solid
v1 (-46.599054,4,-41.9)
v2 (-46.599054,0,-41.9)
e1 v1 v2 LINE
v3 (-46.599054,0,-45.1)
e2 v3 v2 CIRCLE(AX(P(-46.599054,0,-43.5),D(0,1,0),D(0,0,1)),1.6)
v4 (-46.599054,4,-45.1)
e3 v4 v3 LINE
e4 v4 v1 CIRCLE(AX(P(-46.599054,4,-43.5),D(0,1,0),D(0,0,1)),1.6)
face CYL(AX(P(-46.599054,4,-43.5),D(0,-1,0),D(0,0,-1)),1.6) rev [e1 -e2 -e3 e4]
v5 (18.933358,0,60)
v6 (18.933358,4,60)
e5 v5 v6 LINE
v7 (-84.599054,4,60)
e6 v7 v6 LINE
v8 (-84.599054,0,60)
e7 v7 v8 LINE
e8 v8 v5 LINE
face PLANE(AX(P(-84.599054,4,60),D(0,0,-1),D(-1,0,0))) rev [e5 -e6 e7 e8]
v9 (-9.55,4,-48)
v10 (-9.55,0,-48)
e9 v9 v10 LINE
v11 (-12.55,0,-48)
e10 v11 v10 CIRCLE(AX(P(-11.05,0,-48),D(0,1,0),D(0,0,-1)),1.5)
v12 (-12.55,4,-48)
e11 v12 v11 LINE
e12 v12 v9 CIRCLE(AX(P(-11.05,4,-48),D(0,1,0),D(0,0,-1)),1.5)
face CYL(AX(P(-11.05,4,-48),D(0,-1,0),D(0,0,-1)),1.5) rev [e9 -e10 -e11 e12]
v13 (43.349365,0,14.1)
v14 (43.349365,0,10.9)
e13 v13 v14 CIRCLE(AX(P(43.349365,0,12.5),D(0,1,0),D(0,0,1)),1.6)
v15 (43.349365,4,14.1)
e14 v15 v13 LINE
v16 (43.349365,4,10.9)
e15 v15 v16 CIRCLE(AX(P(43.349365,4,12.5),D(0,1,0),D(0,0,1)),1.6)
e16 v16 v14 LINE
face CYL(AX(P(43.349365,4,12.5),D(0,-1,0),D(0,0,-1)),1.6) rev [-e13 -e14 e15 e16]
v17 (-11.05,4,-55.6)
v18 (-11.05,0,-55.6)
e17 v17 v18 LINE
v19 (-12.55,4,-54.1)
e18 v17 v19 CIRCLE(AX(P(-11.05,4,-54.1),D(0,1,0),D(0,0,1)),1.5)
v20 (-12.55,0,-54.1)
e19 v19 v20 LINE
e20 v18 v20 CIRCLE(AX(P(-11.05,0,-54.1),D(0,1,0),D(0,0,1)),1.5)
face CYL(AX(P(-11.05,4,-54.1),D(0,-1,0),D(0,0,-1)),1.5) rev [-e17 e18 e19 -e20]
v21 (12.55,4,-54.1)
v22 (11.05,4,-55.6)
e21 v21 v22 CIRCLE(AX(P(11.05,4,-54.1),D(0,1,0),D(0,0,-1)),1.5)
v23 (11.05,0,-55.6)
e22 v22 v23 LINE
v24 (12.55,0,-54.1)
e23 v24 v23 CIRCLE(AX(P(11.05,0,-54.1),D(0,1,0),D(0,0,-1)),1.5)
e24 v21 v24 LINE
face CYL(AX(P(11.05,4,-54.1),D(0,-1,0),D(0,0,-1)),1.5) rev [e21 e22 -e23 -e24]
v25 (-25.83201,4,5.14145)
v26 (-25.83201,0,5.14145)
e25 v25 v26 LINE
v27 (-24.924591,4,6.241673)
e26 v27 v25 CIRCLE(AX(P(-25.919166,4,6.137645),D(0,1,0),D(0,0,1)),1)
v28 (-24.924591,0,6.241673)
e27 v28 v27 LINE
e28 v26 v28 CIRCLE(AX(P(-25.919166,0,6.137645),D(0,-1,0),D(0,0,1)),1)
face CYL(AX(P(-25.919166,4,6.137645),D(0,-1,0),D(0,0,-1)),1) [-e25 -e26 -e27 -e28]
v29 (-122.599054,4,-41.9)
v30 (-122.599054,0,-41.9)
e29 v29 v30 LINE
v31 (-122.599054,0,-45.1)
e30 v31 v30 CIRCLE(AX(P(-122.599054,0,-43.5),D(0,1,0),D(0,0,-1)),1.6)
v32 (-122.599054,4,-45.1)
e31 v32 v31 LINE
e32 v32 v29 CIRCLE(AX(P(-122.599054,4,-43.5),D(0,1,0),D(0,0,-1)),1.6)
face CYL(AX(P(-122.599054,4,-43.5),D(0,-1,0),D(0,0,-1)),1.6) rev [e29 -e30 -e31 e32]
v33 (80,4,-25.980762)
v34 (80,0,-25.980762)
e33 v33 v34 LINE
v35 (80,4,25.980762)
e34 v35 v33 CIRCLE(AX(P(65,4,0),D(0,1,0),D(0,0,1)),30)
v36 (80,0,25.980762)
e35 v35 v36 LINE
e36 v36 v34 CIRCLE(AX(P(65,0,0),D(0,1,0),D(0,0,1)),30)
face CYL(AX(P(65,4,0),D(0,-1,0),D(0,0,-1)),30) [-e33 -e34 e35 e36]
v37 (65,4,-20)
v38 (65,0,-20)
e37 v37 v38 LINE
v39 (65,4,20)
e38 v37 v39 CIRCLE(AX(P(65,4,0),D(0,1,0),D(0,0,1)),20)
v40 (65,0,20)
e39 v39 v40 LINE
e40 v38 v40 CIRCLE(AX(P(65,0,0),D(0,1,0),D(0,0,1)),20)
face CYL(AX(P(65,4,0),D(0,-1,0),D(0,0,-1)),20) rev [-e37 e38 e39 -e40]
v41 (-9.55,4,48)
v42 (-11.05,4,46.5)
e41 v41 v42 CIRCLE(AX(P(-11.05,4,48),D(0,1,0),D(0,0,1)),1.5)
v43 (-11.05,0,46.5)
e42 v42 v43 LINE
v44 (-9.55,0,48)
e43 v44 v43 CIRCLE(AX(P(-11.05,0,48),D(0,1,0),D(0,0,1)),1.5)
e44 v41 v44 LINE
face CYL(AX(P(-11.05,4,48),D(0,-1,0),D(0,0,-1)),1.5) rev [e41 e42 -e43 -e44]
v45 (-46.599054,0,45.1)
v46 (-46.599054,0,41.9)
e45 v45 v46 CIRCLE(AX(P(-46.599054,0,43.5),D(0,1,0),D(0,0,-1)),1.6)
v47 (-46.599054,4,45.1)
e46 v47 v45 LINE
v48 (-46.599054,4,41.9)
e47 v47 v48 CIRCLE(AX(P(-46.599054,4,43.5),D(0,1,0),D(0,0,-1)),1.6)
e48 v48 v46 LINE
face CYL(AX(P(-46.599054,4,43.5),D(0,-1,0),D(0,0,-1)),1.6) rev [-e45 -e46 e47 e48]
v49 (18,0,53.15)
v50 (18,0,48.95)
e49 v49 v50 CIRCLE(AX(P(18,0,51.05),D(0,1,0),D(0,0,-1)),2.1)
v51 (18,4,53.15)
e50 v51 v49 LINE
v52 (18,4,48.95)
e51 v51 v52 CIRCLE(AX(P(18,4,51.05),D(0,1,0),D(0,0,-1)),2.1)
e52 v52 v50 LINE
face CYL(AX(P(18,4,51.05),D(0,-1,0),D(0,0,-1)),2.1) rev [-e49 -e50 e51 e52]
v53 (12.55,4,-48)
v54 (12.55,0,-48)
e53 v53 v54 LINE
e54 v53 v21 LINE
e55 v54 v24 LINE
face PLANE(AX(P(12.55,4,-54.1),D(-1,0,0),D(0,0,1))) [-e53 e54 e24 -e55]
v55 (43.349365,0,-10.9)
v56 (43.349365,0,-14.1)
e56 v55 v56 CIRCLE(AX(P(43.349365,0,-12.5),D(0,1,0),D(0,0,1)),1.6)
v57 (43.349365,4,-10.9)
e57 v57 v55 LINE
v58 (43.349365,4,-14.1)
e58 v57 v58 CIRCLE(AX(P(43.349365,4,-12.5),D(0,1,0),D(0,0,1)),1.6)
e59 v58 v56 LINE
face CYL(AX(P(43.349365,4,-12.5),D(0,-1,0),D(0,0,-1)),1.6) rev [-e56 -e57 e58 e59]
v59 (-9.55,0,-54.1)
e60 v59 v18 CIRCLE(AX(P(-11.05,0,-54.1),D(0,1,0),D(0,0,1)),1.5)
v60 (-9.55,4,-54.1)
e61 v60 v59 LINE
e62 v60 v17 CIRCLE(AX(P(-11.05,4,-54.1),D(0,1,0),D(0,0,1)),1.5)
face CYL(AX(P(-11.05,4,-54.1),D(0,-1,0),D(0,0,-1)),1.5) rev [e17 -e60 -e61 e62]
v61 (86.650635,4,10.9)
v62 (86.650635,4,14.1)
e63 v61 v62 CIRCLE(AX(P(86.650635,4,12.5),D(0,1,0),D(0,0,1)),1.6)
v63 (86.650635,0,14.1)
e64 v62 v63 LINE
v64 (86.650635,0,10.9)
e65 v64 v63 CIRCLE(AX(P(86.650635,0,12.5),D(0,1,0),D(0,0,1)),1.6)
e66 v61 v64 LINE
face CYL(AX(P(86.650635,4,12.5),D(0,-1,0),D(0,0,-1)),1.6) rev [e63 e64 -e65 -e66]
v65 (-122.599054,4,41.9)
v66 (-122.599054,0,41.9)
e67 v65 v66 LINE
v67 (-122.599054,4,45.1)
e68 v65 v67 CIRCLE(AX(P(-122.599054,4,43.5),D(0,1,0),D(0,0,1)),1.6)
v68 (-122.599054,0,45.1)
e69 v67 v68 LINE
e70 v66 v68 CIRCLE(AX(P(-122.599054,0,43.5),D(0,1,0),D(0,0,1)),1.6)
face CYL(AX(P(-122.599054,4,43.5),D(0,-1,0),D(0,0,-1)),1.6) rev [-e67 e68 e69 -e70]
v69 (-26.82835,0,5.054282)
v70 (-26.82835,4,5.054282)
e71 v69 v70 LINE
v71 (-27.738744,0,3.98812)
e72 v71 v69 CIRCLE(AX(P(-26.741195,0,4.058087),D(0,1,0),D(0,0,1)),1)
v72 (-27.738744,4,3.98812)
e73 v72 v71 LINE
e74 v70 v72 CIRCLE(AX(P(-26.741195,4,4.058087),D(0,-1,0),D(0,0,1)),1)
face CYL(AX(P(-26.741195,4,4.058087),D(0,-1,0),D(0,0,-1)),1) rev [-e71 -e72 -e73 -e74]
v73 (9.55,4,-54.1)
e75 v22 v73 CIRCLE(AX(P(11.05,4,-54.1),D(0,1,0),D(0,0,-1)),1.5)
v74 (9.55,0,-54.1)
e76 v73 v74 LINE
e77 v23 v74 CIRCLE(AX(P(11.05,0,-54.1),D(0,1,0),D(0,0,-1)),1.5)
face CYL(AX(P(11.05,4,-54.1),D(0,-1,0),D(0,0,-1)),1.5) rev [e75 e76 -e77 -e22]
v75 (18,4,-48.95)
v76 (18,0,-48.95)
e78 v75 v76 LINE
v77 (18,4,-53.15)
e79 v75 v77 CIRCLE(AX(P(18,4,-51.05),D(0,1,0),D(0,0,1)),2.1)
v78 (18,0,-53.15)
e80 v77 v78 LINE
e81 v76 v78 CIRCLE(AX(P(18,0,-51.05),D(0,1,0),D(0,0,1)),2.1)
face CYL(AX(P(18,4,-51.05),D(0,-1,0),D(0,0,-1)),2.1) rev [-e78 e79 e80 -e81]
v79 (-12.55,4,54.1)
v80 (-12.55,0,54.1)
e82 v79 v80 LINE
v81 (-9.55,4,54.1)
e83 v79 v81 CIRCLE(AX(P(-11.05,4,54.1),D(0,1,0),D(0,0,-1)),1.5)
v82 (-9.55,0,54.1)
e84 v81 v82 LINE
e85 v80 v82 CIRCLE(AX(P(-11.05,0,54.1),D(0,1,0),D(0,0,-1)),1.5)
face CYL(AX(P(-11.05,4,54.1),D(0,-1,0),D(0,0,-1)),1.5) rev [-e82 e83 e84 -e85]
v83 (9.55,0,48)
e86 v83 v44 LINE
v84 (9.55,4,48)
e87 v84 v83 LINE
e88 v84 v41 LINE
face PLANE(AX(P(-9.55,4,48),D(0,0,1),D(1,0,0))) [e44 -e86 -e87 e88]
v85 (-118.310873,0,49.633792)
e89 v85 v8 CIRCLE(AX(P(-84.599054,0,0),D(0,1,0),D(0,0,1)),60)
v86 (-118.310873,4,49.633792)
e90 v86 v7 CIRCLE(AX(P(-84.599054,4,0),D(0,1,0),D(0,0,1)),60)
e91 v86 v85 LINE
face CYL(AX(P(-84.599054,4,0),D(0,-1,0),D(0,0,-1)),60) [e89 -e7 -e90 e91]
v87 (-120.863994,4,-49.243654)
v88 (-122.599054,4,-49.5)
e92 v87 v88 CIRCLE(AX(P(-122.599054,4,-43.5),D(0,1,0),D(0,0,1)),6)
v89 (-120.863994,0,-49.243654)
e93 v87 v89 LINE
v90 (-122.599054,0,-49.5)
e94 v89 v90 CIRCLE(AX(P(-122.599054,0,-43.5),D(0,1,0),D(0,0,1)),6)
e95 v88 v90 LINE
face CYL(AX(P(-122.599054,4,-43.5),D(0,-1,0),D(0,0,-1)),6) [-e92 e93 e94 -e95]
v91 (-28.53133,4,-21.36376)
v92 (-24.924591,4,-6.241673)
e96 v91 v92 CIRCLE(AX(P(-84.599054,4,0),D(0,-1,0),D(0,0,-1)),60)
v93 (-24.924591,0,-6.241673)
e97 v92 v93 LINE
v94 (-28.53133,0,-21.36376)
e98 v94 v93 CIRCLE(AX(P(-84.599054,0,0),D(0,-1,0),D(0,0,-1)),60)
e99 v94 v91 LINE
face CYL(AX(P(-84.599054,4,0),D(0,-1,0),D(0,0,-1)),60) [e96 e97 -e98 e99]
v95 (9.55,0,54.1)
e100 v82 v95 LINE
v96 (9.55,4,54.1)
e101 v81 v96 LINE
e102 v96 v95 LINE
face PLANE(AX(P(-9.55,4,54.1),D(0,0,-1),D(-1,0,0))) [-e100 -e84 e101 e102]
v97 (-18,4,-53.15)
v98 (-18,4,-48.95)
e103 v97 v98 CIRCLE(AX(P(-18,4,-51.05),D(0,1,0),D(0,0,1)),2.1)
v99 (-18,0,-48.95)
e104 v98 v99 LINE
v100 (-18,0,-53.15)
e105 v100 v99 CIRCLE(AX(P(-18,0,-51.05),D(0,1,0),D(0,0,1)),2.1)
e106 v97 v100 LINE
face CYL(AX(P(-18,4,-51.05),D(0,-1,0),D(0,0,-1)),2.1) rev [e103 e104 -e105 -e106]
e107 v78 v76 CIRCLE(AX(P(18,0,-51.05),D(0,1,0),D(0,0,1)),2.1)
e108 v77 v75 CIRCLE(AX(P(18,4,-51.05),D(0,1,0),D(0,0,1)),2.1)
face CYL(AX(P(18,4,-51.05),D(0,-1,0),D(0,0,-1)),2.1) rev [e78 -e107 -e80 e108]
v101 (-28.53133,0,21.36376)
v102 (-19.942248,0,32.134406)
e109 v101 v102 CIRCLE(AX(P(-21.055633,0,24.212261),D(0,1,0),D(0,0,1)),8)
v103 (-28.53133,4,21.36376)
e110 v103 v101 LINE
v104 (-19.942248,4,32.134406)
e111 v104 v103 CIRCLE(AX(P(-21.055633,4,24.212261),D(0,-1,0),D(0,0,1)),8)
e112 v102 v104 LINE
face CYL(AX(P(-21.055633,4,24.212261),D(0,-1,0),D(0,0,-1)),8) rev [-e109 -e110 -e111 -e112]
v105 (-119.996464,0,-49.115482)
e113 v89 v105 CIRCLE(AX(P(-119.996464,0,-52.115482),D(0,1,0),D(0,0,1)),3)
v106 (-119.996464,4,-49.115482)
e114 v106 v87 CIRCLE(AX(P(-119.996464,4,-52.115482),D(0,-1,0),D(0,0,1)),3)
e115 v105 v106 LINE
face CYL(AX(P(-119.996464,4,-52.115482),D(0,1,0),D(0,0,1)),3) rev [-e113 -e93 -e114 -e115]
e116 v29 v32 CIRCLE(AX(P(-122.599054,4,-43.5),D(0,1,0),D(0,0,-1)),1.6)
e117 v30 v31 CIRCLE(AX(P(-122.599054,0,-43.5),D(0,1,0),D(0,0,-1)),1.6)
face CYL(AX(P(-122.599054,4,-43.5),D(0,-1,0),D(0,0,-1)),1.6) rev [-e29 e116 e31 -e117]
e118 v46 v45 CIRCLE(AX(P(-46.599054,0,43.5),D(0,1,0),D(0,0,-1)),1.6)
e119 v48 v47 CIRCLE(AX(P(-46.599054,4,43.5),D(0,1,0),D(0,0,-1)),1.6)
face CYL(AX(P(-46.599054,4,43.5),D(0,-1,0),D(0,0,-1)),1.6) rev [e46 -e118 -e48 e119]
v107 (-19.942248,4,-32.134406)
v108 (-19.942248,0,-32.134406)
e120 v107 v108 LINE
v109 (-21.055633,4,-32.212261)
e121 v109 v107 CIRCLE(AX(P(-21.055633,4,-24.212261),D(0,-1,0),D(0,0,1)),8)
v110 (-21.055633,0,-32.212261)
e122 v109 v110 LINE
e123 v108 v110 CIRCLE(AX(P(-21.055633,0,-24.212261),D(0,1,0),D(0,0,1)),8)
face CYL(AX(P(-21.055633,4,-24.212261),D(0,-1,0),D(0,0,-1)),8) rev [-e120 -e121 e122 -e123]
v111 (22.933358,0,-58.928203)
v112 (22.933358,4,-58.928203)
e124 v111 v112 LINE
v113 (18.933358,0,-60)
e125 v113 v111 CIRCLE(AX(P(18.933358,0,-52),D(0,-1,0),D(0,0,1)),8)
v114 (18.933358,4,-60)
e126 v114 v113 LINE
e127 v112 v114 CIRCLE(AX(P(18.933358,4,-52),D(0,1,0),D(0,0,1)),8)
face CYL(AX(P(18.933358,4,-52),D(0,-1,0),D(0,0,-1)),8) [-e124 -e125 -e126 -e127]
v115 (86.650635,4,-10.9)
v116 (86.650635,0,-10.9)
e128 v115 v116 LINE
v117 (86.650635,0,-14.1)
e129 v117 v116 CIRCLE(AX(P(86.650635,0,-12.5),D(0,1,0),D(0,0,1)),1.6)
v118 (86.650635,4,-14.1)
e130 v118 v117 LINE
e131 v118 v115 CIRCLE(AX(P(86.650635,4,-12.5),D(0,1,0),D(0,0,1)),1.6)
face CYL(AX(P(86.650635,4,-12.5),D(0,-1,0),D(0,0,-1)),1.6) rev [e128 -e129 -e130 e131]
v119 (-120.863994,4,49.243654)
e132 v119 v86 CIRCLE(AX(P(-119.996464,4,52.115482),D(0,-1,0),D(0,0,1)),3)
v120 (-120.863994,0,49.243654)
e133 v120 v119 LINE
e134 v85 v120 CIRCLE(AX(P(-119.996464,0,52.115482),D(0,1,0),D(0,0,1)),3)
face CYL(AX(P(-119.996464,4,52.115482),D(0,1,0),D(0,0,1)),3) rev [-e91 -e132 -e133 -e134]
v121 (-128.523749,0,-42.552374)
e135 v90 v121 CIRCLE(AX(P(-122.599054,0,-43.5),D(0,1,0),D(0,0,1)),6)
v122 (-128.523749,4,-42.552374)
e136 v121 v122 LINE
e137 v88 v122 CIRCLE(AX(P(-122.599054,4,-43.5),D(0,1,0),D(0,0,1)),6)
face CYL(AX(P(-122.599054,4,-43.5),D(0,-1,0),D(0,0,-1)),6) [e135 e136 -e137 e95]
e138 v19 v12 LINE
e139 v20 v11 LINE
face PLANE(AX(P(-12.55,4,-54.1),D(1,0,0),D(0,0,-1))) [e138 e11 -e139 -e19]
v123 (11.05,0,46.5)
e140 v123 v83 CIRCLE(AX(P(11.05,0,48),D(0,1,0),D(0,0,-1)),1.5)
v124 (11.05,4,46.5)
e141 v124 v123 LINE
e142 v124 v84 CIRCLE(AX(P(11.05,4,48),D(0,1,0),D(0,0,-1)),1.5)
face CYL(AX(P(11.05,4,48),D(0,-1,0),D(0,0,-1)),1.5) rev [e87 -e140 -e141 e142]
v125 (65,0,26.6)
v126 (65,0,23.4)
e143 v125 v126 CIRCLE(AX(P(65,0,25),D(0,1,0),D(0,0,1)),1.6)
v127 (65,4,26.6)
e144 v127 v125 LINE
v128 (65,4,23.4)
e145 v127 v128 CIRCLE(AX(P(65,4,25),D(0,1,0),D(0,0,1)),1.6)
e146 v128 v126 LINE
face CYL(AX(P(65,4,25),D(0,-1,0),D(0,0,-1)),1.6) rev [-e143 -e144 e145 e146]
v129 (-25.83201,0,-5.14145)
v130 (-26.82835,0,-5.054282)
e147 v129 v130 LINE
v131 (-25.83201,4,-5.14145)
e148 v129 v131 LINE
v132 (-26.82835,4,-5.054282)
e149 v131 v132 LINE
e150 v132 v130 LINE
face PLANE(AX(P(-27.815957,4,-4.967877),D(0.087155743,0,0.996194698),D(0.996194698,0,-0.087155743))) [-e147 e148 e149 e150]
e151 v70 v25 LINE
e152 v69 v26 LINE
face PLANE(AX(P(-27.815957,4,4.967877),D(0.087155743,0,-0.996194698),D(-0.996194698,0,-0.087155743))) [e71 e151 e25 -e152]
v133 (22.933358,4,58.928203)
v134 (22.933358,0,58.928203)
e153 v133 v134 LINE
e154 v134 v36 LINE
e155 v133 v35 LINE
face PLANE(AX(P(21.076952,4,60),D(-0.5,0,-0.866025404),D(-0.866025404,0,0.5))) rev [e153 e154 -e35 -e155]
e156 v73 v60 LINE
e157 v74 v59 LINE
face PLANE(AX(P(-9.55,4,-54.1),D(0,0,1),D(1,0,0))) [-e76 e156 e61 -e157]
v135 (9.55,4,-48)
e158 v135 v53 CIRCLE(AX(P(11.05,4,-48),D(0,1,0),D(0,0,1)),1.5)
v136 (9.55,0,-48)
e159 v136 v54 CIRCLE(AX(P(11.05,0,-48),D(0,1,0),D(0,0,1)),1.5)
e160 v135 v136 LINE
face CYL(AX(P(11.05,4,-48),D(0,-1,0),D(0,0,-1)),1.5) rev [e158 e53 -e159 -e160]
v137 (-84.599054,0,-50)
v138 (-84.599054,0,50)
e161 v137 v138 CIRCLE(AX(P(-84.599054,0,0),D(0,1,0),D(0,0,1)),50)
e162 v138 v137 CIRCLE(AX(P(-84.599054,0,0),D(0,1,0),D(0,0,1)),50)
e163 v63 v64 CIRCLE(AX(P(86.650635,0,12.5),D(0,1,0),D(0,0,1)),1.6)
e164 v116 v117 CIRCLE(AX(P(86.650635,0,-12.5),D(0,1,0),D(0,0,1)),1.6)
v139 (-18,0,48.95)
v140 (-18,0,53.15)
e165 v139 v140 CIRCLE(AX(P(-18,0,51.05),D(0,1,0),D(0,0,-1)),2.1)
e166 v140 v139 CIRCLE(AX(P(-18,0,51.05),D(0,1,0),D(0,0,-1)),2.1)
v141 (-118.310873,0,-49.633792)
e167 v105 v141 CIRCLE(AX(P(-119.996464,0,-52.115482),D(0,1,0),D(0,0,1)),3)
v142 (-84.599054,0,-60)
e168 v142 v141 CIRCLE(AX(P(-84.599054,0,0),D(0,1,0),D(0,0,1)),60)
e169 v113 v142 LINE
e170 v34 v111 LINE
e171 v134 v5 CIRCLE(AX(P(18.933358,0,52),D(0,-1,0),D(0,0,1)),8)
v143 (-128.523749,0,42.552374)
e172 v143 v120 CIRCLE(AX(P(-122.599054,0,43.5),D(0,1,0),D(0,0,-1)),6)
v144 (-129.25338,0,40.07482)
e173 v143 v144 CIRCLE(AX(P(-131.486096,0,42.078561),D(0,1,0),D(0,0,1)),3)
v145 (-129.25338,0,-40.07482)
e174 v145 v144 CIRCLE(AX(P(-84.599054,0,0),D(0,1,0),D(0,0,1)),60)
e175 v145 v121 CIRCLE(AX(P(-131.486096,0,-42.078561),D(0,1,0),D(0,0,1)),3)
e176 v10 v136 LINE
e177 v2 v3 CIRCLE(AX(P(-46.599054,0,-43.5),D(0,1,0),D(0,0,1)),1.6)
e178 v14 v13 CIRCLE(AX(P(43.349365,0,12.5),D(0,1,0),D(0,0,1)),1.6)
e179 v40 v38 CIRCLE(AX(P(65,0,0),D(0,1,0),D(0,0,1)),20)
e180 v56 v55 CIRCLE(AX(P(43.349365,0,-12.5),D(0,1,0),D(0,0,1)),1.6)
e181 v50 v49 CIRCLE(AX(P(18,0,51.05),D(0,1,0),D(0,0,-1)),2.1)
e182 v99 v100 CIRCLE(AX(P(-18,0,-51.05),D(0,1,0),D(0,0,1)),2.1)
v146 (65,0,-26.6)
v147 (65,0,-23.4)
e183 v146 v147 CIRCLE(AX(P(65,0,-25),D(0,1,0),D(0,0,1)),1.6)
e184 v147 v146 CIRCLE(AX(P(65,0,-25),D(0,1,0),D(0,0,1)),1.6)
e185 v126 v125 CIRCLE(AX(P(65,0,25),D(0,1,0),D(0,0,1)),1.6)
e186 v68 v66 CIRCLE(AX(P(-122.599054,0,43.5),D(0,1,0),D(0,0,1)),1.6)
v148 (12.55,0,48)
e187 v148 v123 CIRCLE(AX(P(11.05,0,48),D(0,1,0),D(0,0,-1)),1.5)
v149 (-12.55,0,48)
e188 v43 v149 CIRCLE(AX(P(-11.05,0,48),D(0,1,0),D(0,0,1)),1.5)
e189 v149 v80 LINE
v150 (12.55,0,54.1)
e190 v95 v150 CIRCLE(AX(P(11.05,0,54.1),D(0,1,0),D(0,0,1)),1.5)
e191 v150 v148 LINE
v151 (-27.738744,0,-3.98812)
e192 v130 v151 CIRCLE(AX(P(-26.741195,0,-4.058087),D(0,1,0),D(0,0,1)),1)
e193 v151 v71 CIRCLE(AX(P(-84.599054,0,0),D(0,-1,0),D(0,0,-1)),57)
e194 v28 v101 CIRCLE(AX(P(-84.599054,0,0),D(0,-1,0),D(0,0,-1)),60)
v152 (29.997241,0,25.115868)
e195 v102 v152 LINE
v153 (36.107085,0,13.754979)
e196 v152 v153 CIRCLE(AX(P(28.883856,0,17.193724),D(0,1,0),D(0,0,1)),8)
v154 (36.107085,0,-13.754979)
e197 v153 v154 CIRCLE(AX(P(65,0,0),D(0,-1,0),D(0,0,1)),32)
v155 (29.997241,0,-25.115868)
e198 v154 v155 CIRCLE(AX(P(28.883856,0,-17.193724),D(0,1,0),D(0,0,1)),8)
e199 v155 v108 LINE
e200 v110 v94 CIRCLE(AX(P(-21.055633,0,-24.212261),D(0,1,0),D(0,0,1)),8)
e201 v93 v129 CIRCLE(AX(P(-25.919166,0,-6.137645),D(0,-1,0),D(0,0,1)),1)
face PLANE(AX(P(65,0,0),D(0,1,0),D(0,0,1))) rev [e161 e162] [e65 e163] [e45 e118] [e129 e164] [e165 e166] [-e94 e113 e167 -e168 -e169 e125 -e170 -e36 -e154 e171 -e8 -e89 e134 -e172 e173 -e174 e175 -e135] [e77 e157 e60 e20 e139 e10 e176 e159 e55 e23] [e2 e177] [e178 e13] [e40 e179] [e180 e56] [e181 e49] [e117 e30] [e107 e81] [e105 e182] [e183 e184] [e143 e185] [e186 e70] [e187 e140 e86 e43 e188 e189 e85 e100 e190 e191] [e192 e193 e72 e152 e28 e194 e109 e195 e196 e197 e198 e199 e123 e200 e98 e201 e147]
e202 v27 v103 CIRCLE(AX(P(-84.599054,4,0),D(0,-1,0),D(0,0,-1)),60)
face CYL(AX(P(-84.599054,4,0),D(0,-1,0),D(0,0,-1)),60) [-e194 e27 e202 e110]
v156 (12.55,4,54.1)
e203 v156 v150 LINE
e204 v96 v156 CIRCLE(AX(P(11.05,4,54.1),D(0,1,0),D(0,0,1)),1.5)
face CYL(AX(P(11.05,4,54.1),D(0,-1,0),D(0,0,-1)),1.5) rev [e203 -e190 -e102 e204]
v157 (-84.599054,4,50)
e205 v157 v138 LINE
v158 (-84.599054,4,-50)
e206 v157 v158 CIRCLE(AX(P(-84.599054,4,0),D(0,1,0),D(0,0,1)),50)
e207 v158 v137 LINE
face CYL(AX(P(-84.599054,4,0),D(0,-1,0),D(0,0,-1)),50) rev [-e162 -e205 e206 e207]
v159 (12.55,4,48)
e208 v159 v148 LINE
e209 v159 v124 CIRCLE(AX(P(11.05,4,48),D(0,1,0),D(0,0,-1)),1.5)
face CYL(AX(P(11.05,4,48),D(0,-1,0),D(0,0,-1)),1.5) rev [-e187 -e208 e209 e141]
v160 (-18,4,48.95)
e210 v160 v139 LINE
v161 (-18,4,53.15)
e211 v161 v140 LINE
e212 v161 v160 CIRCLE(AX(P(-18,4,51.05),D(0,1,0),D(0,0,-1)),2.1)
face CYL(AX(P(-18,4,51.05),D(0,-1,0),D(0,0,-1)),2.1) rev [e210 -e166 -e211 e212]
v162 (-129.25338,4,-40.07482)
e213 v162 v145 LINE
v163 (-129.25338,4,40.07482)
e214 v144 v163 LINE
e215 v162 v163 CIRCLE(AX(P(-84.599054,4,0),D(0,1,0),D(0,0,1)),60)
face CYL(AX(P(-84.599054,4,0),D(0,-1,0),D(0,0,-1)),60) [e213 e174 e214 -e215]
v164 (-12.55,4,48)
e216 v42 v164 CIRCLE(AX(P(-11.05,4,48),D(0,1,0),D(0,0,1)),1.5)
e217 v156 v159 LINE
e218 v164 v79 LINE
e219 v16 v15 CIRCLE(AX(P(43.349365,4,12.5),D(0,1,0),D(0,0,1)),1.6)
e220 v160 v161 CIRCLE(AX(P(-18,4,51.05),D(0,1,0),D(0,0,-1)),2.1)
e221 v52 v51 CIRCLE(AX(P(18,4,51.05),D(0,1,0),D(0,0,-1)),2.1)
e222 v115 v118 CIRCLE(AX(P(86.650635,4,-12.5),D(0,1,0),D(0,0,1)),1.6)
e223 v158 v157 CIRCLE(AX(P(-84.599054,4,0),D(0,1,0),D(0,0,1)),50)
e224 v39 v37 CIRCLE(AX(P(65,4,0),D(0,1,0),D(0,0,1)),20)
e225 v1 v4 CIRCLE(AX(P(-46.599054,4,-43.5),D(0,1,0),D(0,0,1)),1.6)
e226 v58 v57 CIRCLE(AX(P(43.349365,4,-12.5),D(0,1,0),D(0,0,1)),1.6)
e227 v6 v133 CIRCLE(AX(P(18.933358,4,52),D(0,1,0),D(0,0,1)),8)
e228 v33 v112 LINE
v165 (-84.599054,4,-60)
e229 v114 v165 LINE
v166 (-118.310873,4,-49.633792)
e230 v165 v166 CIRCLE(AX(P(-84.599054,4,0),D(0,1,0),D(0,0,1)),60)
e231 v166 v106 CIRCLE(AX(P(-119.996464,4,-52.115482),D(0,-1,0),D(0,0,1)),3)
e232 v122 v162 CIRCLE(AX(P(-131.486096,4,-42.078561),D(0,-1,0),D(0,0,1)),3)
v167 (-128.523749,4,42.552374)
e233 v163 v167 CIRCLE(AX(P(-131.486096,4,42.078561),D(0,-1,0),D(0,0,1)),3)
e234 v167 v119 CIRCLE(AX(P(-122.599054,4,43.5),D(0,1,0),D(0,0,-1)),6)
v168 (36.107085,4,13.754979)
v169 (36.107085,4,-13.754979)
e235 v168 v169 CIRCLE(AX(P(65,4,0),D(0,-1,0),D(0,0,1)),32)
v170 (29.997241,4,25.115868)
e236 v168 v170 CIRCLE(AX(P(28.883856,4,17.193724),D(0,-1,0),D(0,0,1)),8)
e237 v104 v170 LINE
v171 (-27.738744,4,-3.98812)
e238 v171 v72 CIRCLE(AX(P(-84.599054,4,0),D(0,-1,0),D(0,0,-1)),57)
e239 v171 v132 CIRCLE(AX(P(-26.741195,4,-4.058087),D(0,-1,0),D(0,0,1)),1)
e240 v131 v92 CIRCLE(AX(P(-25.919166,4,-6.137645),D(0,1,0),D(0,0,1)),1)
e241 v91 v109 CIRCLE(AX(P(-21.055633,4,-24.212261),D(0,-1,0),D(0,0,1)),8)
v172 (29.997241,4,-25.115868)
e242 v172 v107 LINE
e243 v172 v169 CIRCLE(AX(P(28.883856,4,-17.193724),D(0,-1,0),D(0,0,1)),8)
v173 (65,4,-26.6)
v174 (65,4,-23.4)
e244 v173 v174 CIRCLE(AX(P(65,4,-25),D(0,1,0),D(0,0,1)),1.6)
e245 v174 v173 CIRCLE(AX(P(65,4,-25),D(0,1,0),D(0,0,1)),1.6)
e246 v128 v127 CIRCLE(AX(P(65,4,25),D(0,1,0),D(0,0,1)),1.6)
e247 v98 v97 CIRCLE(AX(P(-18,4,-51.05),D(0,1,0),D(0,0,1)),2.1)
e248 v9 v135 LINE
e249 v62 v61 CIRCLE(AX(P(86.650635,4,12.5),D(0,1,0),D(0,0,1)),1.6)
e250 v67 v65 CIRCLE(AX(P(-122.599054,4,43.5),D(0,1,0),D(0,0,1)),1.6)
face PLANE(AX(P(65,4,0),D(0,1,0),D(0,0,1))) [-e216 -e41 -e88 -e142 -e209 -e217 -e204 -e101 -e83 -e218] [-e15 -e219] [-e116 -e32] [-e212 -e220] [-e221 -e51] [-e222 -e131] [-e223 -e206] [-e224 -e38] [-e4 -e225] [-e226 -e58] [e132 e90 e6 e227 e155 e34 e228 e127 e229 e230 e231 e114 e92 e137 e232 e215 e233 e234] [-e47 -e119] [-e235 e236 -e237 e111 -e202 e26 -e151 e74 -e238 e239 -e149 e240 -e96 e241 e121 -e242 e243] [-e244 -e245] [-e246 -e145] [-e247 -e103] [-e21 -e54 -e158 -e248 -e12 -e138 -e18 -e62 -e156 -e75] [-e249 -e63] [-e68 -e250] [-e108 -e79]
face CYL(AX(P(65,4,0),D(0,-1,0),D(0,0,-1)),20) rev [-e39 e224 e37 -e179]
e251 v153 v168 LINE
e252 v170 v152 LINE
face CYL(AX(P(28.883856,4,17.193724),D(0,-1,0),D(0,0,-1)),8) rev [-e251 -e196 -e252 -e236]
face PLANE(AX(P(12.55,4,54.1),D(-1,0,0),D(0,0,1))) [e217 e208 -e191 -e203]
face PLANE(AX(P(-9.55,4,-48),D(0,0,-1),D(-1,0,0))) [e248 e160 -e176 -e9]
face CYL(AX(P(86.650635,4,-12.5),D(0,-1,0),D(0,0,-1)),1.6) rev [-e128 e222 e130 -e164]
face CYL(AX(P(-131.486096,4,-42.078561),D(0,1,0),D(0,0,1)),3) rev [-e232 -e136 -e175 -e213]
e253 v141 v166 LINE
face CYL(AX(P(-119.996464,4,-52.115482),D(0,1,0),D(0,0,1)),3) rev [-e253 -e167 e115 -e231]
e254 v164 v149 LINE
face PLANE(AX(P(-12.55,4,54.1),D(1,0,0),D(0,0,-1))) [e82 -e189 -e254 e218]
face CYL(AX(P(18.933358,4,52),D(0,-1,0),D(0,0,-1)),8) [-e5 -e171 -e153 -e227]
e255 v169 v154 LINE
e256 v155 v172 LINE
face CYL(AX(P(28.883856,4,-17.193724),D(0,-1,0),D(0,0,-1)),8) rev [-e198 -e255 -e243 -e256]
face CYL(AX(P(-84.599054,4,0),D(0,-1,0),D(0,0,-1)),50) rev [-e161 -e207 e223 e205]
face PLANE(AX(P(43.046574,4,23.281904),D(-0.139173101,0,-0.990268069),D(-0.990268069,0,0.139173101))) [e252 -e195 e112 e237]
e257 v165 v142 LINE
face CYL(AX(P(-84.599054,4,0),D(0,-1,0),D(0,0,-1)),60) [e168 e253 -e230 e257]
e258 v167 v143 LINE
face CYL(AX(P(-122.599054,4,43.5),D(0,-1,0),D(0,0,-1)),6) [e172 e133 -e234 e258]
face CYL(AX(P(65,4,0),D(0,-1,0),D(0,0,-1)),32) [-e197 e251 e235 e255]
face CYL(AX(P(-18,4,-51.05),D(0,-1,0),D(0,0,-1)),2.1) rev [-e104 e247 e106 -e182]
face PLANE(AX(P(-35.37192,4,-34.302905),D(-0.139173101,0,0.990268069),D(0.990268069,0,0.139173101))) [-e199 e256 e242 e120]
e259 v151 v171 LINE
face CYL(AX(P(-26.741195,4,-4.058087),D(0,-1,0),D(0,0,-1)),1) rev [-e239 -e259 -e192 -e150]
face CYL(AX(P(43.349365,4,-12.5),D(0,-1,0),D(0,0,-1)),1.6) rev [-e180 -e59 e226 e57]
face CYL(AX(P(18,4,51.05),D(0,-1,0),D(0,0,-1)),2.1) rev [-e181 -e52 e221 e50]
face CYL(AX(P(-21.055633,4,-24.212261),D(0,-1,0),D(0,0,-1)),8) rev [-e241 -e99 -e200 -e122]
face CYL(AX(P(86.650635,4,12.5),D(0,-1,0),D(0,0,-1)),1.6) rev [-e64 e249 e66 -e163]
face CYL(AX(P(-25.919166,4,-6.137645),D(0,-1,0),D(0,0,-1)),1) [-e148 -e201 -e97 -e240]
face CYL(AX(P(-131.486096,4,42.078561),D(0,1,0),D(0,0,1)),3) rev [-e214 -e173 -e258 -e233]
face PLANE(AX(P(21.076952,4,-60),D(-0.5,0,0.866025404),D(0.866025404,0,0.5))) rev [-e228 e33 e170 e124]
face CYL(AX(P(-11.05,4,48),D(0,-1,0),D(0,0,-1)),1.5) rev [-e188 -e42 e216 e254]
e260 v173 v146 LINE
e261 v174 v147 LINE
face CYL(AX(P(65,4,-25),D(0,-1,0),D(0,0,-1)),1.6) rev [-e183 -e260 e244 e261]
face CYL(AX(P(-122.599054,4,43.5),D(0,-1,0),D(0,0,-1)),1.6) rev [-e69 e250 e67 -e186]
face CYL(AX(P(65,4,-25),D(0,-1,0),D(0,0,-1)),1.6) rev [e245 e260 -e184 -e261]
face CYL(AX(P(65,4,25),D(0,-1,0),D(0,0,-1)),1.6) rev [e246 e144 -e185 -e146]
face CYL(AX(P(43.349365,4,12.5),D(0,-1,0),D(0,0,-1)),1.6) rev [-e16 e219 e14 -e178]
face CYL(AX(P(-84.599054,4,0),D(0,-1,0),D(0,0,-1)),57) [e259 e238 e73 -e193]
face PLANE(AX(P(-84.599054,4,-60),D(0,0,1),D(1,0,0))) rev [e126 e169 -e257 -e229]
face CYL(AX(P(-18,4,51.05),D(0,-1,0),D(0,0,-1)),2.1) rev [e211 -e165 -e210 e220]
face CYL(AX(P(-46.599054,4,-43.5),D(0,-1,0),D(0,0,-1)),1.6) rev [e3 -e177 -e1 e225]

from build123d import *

# Parameters (mm, degrees)
SKETCH_1_R      = 50
SKETCH_1_R_2    = 20
SKETCH_1_R_3    = 1.6
SKETCH_1_R_4    = 2.1
EXTRUDE_1_DEPTH = 4
FILLET_R8_1_R   = 8
FILLET_R2_2_R   = 1
FILLET_R3_R     = 3


with BuildPart() as part:
    # 草图1 → 凸台-拉伸1 (new body)
    with BuildSketch(Plane(origin=(0, 0, 0), x_dir=(1, 0, 0), z_dir=(0, 1, 0))):
        with BuildLine():
            Line((21.076951546, 60), (80, 25.980762114))
            ThreePointArc((80, 25.980762114), (95, 0), (80, -25.980762114))
            Line((80, -25.980762114), (21.076951546, -60))
            Line((21.076951546, -60), (-84.599054368, -60))
            ThreePointArc((-84.599054368, -60), (-103.000462095, -57.108564977), (-119.628320662, -48.712939789))
            ThreePointArc((-119.628320662, -48.712939789), (-126.546403622, -48.018676119), (-128.163868254, -41.256599364))
            ThreePointArc((-128.163868254, -41.256599364), (-144.599054368, 0), (-128.163868254, 41.256599364))
            ThreePointArc((-128.163868254, 41.256599364), (-126.546403622, 48.018676119), (-119.628320662, 48.712939789))
            ThreePointArc((-119.628320662, 48.712939789), (-103.000462095, 57.108564977), (-84.599054368, 60))
            Line((-84.599054368, 60), (21.076951546, 60))
        make_face()
        with Locations(Location((-84.599054368, 0, 0), (0, 0, 270))):
            Circle(SKETCH_1_R, mode=Mode.SUBTRACT)
        with Locations(Location((65, 0, 0), (0, 0, 270))):
            Circle(SKETCH_1_R_2, mode=Mode.SUBTRACT)
        with Locations(Location((65, 25, 0), (0, 0, 270))):
            Circle(SKETCH_1_R_3, mode=Mode.SUBTRACT)
        with Locations(Location((86.650635095, 12.5, 0), (0, 0, 270))):
            Circle(SKETCH_1_R_3, mode=Mode.SUBTRACT)
        with Locations(Location((86.650635095, -12.5, 0), (0, 0, 270))):
            Circle(SKETCH_1_R_3, mode=Mode.SUBTRACT)
        with Locations(Location((65, -25, 0), (0, 0, 270))):
            Circle(SKETCH_1_R_3, mode=Mode.SUBTRACT)
        with Locations(Location((43.349364905, -12.5, 0), (0, 0, 270))):
            Circle(SKETCH_1_R_3, mode=Mode.SUBTRACT)
        with Locations(Location((43.349364905, 12.5, 0), (0, 0, 270))):
            Circle(SKETCH_1_R_3, mode=Mode.SUBTRACT)
        with Locations(Location((-18, 51.05, 0), (0, 0, 270))):
            Circle(SKETCH_1_R_4, mode=Mode.SUBTRACT)
        with Locations(Location((18, 51.05, 0), (0, 0, 270))):
            Circle(SKETCH_1_R_4, mode=Mode.SUBTRACT)
        with Locations(Location((-18, -51.05, 0), (0, 0, 90))):
            Circle(SKETCH_1_R_4, mode=Mode.SUBTRACT)
        with Locations(Location((18, -51.05, 0), (0, 0, 90))):
            Circle(SKETCH_1_R_4, mode=Mode.SUBTRACT)
        with Locations(Location((-46.599054368, 43.5, 0), (0, 0, 270))):
            Circle(SKETCH_1_R_3, mode=Mode.SUBTRACT)
        with Locations(Location((-122.599054368, 43.5, 0), (0, 0, 90))):
            Circle(SKETCH_1_R_3, mode=Mode.SUBTRACT)
        with Locations(Location((-46.599054368, -43.5, 0), (0, 0, 90))):
            Circle(SKETCH_1_R_3, mode=Mode.SUBTRACT)
        with Locations(Location((-122.599054368, -43.5, 0), (0, 0, 270))):
            Circle(SKETCH_1_R_3, mode=Mode.SUBTRACT)
        with BuildLine():
            Line((-9.55, 54.1), (9.55, 54.1))
            ThreePointArc((9.55, 54.1), (11.05, 55.6), (12.55, 54.1))
            Line((12.55, 54.1), (12.55, 48))
            ThreePointArc((12.55, 48), (11.05, 46.5), (9.55, 48))
            Line((9.55, 48), (-9.55, 48))
            ThreePointArc((-9.55, 48), (-11.05, 46.5), (-12.55, 48))
            Line((-12.55, 48), (-12.55, 54.1))
            ThreePointArc((-12.55, 54.1), (-11.05, 55.6), (-9.55, 54.1))
        make_face(mode=Mode.SUBTRACT)
        with BuildLine():
            Line((-9.55, -48), (9.55, -48))
            ThreePointArc((9.55, -48), (11.05, -46.5), (12.55, -48))
            Line((12.55, -48), (12.55, -54.1))
            ThreePointArc((12.55, -54.1), (11.05, -55.6), (9.55, -54.1))
            Line((9.55, -54.1), (-9.55, -54.1))
            ThreePointArc((-9.55, -54.1), (-11.05, -55.6), (-12.55, -54.1))
            Line((-12.55, -54.1), (-12.55, -48))
            ThreePointArc((-12.55, -48), (-11.05, -46.5), (-9.55, -48))
        make_face(mode=Mode.SUBTRACT)
        with BuildLine():
            Line((-35.371920456, 34.302904932), (43.046573591, 23.281904323))
            ThreePointArc((43.046573591, 23.281904323), (33, 0), (43.046573591, -23.281904323))
            Line((43.046573591, -23.281904323), (-35.371920456, -34.302904932))
            ThreePointArc((-35.371920456, -34.302904932), (-28.194236848, -20.457188481), (-24.827372483, -5.229344565))
            Line((-24.827372483, -5.229344565), (-27.815956577, -4.967877337))
            ThreePointArc((-27.815956577, -4.967877337), (-27.599054368, 0), (-27.815956577, 4.967877337))
            Line((-27.815956577, 4.967877337), (-24.827372483, 5.229344565))
            ThreePointArc((-24.827372483, 5.229344565), (-28.194236848, 20.457188481), (-35.371920456, 34.302904932))
        make_face(mode=Mode.SUBTRACT)
    extrude(amount=EXTRUDE_1_DEPTH)

    # R8 圆角1
    fillet_r8_1_edges = [part.edges().sort_by_distance(p)[0] for p in [
        (-35.371920456, 2, -34.302904932),
        (-35.371920456, 2, 34.302904932),
        (43.046573591, 2, 23.281904323),
        (43.046573591, 2, -23.281904323),
        (21.076951546, 2, -60),
        (21.076951546, 2, 60),
    ]]
    fillet(fillet_r8_1_edges, radius=FILLET_R8_1_R)

    # R2 圆角2
    fillet_r2_2_edges = [part.edges().sort_by_distance(p)[0] for p in [
        (-24.827372483, 2, -5.229344565),
        (-27.815956577, 2, -4.967877337),
        (-27.815956577, 2, 4.967877337),
        (-24.827372483, 2, 5.229344565),
    ]]
    fillet(fillet_r2_2_edges, radius=FILLET_R2_2_R)

    # R3 圆角
    fillet_r3_edges = [part.edges().sort_by_distance(p)[0] for p in [
        (-119.628320662, 2, 48.712939789),
        (-128.163868254, 2, 41.256599364),
        (-128.163868254, 2, -41.256599364),
        (-119.628320662, 2, -48.712939789),
    ]]
    fillet(fillet_r3_edges, radius=FILLET_R3_R)


solid = part.part
